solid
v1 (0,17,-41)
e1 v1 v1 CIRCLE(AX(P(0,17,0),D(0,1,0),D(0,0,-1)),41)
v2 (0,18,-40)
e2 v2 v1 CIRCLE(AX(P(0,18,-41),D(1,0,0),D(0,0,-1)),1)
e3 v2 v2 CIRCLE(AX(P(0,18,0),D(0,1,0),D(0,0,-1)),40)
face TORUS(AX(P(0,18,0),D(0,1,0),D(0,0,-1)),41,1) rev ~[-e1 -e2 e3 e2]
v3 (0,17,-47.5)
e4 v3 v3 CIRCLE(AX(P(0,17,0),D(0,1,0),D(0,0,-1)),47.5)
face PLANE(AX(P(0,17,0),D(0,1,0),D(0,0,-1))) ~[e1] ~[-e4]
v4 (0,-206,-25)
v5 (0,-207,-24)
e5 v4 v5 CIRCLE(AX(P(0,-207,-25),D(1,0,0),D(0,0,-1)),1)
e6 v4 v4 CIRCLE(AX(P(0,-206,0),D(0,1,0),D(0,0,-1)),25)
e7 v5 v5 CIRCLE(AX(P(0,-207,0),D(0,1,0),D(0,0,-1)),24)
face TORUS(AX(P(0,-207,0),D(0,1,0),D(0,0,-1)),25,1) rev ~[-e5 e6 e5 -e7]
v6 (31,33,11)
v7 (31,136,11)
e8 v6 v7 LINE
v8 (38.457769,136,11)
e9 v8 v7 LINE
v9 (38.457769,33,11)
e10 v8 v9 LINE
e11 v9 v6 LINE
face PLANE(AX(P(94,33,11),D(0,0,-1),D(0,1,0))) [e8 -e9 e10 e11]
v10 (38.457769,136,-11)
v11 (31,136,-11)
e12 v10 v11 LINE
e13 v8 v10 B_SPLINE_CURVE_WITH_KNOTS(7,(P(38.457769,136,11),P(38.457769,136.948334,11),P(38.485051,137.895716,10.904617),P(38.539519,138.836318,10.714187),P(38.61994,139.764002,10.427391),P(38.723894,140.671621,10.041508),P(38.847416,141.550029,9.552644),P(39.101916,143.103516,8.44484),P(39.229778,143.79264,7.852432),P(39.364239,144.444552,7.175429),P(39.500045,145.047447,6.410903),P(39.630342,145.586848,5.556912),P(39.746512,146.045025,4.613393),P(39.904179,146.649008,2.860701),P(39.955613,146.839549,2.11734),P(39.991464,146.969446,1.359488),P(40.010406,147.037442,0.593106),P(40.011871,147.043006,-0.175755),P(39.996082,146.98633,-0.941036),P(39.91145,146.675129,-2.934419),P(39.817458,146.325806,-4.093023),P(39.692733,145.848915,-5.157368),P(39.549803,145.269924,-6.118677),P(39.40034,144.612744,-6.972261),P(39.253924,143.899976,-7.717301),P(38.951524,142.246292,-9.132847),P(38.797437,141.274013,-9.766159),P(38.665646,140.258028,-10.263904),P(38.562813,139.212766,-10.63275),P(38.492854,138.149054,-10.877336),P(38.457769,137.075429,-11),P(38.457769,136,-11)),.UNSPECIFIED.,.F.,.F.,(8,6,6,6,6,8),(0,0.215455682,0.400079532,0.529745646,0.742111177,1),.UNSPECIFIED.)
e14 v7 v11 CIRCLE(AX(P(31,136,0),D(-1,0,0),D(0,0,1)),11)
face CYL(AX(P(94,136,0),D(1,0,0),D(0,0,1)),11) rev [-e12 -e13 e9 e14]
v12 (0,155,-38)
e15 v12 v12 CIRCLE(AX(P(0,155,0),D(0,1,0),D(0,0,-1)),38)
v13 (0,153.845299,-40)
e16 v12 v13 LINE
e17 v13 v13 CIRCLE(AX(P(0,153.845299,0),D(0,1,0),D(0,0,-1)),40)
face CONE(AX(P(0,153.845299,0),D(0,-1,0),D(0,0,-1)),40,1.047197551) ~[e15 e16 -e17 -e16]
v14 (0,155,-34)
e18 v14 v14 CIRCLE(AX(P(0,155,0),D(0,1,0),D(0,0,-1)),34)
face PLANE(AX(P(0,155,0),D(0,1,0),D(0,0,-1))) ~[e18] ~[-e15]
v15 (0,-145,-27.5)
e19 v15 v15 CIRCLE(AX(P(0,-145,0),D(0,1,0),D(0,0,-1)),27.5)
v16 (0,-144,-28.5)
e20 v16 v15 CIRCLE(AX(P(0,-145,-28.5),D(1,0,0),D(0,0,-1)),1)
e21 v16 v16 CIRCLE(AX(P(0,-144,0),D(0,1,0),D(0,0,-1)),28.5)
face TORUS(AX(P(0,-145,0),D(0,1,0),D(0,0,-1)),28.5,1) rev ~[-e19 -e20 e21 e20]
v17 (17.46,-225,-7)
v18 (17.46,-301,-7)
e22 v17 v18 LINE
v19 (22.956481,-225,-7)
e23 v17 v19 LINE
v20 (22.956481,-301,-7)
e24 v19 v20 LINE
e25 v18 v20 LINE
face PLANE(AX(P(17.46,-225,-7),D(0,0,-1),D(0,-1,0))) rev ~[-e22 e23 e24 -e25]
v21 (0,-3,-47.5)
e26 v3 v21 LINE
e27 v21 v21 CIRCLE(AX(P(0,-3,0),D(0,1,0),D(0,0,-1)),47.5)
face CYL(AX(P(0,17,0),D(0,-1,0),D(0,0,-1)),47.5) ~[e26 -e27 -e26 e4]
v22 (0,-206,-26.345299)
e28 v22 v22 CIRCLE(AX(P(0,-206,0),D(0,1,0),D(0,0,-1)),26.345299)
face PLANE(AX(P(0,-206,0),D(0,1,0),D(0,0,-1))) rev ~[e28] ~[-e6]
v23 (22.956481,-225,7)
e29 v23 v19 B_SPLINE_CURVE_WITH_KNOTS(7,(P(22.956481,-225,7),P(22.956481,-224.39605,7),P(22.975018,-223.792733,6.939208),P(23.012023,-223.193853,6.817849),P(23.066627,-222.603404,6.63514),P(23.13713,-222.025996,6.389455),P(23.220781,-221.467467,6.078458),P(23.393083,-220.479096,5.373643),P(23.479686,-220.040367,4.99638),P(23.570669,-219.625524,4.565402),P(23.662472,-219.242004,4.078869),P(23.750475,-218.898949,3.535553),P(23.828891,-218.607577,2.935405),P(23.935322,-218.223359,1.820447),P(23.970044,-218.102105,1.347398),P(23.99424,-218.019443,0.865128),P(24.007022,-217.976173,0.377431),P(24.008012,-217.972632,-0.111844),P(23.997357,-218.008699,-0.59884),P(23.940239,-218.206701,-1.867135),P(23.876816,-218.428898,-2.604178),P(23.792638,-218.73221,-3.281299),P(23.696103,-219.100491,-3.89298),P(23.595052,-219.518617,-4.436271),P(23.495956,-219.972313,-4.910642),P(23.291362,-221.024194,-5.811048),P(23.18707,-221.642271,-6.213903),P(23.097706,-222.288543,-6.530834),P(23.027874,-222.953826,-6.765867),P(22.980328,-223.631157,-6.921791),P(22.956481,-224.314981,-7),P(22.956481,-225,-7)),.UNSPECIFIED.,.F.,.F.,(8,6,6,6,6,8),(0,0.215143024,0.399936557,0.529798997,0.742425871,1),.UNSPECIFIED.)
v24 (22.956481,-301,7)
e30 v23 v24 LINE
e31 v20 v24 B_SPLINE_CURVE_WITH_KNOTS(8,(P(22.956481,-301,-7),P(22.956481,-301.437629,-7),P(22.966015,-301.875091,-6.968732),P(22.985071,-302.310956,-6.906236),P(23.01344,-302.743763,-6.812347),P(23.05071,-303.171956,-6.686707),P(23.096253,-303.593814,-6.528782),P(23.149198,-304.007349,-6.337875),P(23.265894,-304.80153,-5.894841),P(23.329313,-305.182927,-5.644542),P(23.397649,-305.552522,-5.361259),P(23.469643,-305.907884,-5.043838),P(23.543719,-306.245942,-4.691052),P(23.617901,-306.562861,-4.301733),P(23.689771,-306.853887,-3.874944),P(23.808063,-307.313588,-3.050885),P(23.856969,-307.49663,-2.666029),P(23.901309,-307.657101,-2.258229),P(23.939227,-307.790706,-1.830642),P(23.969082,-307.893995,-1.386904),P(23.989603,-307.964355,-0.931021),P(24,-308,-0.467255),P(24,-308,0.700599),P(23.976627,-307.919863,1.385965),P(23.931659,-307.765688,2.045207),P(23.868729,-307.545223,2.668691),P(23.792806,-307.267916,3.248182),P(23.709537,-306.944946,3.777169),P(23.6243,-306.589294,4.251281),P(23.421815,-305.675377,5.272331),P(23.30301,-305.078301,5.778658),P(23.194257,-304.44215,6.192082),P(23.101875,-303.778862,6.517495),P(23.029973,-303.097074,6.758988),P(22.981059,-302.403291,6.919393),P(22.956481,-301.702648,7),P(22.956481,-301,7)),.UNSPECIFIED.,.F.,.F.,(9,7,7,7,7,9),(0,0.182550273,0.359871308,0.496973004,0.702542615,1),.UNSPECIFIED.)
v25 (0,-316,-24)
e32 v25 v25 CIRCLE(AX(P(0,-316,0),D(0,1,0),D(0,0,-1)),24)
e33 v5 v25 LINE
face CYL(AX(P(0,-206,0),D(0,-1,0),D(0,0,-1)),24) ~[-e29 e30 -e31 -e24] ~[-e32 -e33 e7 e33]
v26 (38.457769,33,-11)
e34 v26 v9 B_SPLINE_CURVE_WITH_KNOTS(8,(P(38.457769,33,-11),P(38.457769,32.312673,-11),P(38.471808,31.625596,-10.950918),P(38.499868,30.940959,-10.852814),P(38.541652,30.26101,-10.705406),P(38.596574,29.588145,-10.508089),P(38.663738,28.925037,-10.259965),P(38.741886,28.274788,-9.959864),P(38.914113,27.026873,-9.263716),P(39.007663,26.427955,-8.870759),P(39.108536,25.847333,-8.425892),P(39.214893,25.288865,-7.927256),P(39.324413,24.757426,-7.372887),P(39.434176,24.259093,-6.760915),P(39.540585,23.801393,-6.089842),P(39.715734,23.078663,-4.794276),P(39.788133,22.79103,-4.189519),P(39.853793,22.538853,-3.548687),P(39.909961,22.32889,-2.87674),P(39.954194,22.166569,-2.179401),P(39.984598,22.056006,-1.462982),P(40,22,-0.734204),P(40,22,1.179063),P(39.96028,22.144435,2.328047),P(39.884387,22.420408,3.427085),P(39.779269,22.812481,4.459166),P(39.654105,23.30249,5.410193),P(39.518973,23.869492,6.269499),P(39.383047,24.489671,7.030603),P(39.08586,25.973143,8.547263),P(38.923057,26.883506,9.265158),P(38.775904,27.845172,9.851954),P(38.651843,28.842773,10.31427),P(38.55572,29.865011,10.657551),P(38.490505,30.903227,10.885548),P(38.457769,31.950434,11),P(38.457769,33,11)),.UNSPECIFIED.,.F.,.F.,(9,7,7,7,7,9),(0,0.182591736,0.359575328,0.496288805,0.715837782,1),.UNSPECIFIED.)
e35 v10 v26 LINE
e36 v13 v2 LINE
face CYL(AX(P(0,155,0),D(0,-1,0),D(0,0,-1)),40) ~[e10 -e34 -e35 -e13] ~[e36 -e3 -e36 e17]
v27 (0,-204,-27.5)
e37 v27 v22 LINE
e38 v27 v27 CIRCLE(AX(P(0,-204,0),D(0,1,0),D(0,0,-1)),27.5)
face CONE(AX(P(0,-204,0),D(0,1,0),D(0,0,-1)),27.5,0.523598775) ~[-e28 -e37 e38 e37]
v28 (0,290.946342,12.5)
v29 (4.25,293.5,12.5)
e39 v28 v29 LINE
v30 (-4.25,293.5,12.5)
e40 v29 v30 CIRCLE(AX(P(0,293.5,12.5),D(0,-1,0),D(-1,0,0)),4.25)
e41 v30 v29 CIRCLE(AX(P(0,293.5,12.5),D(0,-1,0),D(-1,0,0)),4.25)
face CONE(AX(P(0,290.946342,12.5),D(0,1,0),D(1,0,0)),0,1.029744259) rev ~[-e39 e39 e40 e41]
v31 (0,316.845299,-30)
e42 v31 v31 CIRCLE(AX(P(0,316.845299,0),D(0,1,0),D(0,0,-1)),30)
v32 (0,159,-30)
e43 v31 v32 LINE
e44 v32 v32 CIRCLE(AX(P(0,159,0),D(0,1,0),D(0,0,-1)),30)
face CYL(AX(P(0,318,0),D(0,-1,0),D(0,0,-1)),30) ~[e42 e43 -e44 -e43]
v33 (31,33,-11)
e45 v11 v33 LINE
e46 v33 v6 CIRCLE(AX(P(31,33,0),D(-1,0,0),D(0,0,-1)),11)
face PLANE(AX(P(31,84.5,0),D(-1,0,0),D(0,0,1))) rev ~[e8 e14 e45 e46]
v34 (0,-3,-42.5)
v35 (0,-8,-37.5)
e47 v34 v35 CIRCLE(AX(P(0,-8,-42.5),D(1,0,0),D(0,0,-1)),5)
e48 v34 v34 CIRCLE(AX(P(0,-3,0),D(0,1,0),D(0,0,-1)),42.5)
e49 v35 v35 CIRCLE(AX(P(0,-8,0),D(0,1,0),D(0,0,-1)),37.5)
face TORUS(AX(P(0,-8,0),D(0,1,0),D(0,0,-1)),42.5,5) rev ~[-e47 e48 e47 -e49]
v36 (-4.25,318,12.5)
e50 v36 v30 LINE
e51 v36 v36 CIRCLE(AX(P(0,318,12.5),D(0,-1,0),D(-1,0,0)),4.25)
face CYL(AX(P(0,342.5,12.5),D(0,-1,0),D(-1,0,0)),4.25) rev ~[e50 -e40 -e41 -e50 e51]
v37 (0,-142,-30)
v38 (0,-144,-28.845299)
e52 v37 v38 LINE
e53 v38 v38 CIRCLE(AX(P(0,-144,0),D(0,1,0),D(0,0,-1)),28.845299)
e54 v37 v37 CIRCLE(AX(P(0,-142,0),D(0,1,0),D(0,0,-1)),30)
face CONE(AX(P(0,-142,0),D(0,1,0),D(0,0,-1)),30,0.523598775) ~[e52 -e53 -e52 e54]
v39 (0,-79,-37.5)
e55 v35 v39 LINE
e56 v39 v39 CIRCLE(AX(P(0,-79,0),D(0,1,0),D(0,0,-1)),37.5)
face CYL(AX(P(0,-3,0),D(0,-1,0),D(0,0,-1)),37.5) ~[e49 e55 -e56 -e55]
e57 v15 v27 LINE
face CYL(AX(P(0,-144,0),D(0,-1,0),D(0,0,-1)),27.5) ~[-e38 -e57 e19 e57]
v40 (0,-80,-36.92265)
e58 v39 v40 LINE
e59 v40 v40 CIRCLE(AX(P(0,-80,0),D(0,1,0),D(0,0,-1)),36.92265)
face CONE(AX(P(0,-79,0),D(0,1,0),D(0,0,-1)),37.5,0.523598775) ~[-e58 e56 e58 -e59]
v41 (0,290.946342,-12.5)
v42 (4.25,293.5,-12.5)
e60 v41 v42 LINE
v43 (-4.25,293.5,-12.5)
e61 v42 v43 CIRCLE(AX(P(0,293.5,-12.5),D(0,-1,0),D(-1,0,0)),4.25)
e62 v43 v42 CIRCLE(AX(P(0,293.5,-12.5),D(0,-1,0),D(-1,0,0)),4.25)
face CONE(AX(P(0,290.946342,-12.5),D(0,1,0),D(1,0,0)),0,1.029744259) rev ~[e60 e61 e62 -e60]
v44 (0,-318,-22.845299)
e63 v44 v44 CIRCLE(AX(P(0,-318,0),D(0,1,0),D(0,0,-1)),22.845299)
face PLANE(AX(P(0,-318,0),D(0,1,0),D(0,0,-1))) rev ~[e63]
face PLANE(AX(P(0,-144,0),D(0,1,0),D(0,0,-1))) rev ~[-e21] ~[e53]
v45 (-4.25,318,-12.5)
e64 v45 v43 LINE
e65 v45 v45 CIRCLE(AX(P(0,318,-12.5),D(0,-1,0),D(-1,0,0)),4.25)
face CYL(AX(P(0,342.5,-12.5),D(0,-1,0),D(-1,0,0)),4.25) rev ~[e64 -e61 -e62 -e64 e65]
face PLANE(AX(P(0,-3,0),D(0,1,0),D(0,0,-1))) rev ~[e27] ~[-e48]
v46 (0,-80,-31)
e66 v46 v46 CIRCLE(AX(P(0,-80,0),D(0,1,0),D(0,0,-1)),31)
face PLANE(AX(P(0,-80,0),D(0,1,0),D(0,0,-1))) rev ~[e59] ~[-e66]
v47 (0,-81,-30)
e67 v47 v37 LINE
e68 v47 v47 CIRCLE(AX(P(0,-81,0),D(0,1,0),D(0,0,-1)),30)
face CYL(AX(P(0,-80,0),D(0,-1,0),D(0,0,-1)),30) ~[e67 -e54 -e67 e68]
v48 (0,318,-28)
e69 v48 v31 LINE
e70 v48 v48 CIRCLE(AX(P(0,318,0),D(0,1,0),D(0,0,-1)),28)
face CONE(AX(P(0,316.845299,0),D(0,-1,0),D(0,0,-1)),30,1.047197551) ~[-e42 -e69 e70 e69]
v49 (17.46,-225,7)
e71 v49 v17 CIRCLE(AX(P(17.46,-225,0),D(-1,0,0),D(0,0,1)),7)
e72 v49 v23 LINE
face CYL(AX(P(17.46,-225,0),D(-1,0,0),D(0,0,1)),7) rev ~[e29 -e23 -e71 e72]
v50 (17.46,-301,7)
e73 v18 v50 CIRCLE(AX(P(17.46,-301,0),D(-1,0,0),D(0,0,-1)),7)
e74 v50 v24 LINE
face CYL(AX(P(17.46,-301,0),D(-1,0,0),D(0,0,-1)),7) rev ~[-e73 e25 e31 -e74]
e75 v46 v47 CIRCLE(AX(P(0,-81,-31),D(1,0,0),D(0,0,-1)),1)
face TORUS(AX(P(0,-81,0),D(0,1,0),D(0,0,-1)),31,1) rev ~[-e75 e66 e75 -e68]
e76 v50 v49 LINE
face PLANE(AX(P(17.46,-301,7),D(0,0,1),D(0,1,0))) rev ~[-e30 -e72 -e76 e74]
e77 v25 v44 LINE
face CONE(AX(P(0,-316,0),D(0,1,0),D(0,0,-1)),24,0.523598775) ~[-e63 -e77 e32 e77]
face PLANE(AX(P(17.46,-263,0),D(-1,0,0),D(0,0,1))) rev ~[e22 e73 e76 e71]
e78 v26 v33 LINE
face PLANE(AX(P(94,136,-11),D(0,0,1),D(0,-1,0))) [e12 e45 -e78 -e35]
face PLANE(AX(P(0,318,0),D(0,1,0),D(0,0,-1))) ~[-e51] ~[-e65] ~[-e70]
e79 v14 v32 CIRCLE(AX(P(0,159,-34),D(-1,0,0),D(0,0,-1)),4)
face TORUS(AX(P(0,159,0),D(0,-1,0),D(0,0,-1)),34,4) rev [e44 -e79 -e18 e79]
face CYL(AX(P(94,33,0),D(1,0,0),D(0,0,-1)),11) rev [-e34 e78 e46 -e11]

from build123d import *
from OCP.BRepFilletAPI import BRepFilletAPI_MakeChamfer

# Parameters (mm, degrees)
CHAMFER1_SIZE          = 2
CHAMFER1_SIZE2         = 1.154700538
FILLET1_R              = 1
FILLET2_R              = 4
FILLET3_R              = 5
CHAMFER2_SIZE          = 1
CHAMFER2_SIZE2         = 0.577350269
CHAMFER3_SIZE          = 2
CHAMFER3_SIZE2         = 1.154700538
CHAMFER4_SIZE          = 2
CHAMFER4_SIZE2         = 1.154700538
M10_TAPPED_HOLE1_D     = 8.5
M10_TAPPED_HOLE1_DEPTH = 24.5
M10_TAPPED_HOLE1_TIP   = 2.553657631
CUT_EXTRUDE1_START     = 94
CUT_EXTRUDE1_DEPTH     = 63
CUT_EXTRUDE2_START     = 17.46
CUT_EXTRUDE2_DEPTH     = 63


with BuildPart() as part:
    # Sketch2 → Revolve1 (revolve)
    with BuildSketch(Plane.XY, mode=Mode.PRIVATE) as revolve1_sk:
        Polygon((0, -318), (0, 318), (30, 318), (30, 155), (40, 155), (40, 17), (47.5, 17), (47.5, -3), (37.5, -3), (37.5, -80), (30, -80), (30, -144), (27.5, -144), (27.5, -206), (24, -206), (24, -318), align=None)
    revolve(revolve1_sk.sketch.rotate(Axis((0, -318, 0), (0, 1, 0)), 90), axis=Axis((0, -318, 0), (0, 1, 0)))

    # Chamfer1: one chamfer whose edges measure the first distance from different faces: ONE call of the kernel's chamfer builder (chamfer() names one face for all edges)
    chamfer1_edges_1 = [part.edges().sort_by_distance(p)[0] for p in [
        (0, -318, 24),
    ]]
    chamfer1_side_1 = [part.faces().sort_by_distance(p)[0] for p in [
        (0, -262, 24),
    ]]
    chamfer1_edges_2 = [part.edges().sort_by_distance(p)[0] for p in [
        (0, 155, 40),
    ]]
    chamfer1_side_2 = [part.faces().sort_by_distance(p)[0] for p in [
        (0, 155, 31.13137085),
    ]]
    chamfer1_edges_3 = [part.edges().sort_by_distance(p)[0] for p in [
        (0, 318, 30),
    ]]
    chamfer1_side_3 = [part.faces().sort_by_distance(p)[0] for p in [
        (0, 318, 0),
    ]]
    chamfer1 = BRepFilletAPI_MakeChamfer(part.part.solid().wrapped)
    for e in chamfer1_edges_1:
        chamfer1.Add(CHAMFER1_SIZE, CHAMFER1_SIZE2, e.wrapped, chamfer1_side_1[0].wrapped)  # the first distance lies on this face
    for e in chamfer1_edges_2:
        chamfer1.Add(CHAMFER1_SIZE, CHAMFER1_SIZE2, e.wrapped, chamfer1_side_2[0].wrapped)  # the first distance lies on this face
    for e in chamfer1_edges_3:
        chamfer1.Add(CHAMFER1_SIZE, CHAMFER1_SIZE2, e.wrapped, chamfer1_side_3[0].wrapped)  # the first distance lies on this face
    add(Compound.cast(chamfer1.Shape()), mode=Mode.REPLACE)

    # Fillet1
    fillet1_edges = [part.edges().sort_by_distance(p)[0] for p in [
        (0, -206, 24),
        (0, -144, 27.5),
        (0, -80, 30),
        (0, 17, 40),
    ]]
    fillet(fillet1_edges, radius=FILLET1_R)

    # Fillet2
    fillet2_edges = [part.edges().sort_by_distance(p)[0] for p in [
        (0, 155, 30),
    ]]
    fillet(fillet2_edges, radius=FILLET2_R)

    # Fillet3
    fillet3_edges = [part.edges().sort_by_distance(p)[0] for p in [
        (0, -3, 37.5),
    ]]
    fillet(fillet3_edges, radius=FILLET3_R)

    # Chamfer2
    chamfer2_edges = [part.edges().sort_by_distance(p)[0] for p in [
        (0, -80, 37.5),
    ]]
    chamfer2_side = [part.faces().sort_by_distance(p)[0] for p in [
        (0, -44, 37.5),
    ]]
    chamfer(chamfer2_edges, length=CHAMFER2_SIZE, length2=CHAMFER2_SIZE2, reference=chamfer2_side[0])

    # Chamfer3
    chamfer3_edges = [part.edges().sort_by_distance(p)[0] for p in [
        (0, -206, 27.5),
    ]]
    chamfer3_side = [part.faces().sort_by_distance(p)[0] for p in [
        (0, -175.5, 27.5),
    ]]
    chamfer(chamfer3_edges, length=CHAMFER3_SIZE, length2=CHAMFER3_SIZE2, reference=chamfer3_side[0])

    # Chamfer4
    chamfer4_edges = [part.edges().sort_by_distance(p)[0] for p in [
        (0, -144, 30),
    ]]
    chamfer4_side = [part.faces().sort_by_distance(p)[0] for p in [
        (0, -112.5, 30),
    ]]
    chamfer(chamfer4_edges, length=CHAMFER4_SIZE, length2=CHAMFER4_SIZE2, reference=chamfer4_side[0])

    # M10 Tapped Hole1
    with Locations(Plane(origin=(0, 318, 0), x_dir=(1, 0, 0), z_dir=(0, 1, 0))):
        with Locations((0, 12.5), (0, -12.5)):
            Hole(M10_TAPPED_HOLE1_D / 2, depth=M10_TAPPED_HOLE1_DEPTH)
            with Locations((0, 0, -(M10_TAPPED_HOLE1_DEPTH + M10_TAPPED_HOLE1_TIP / 2))):  # 118° drill point
                Cone(0, M10_TAPPED_HOLE1_D / 2, M10_TAPPED_HOLE1_TIP, mode=Mode.SUBTRACT)

    # Sketch6 → Cut-Extrude1 (cut)
    with BuildSketch(Plane(origin=(0, 0, 0), x_dir=(0, 0, -1), z_dir=(1, 0, 0)).offset(CUT_EXTRUDE1_START)):
        with BuildLine():
            Line((11, 136), (11, 33))
            ThreePointArc((11, 33), (0, 22), (-11, 33))
            Line((-11, 33), (-11, 136))
            ThreePointArc((-11, 136), (0, 147), (11, 136))
        make_face()
    extrude(amount=-CUT_EXTRUDE1_DEPTH, mode=Mode.SUBTRACT)

    # Sketch8 → Cut-Extrude2 (cut)
    with BuildSketch(Plane(origin=(0, 0, 0), x_dir=(0, 0, -1), z_dir=(1, 0, 0)).offset(CUT_EXTRUDE2_START)):
        with BuildLine():
            Line((-7, -301), (-7, -225))
            ThreePointArc((-7, -225), (0, -218), (7, -225))
            Line((7, -225), (7, -301))
            ThreePointArc((7, -301), (0, -308), (-7, -301))
        make_face()
    extrude(amount=CUT_EXTRUDE2_DEPTH, mode=Mode.SUBTRACT)


solid = part.part
